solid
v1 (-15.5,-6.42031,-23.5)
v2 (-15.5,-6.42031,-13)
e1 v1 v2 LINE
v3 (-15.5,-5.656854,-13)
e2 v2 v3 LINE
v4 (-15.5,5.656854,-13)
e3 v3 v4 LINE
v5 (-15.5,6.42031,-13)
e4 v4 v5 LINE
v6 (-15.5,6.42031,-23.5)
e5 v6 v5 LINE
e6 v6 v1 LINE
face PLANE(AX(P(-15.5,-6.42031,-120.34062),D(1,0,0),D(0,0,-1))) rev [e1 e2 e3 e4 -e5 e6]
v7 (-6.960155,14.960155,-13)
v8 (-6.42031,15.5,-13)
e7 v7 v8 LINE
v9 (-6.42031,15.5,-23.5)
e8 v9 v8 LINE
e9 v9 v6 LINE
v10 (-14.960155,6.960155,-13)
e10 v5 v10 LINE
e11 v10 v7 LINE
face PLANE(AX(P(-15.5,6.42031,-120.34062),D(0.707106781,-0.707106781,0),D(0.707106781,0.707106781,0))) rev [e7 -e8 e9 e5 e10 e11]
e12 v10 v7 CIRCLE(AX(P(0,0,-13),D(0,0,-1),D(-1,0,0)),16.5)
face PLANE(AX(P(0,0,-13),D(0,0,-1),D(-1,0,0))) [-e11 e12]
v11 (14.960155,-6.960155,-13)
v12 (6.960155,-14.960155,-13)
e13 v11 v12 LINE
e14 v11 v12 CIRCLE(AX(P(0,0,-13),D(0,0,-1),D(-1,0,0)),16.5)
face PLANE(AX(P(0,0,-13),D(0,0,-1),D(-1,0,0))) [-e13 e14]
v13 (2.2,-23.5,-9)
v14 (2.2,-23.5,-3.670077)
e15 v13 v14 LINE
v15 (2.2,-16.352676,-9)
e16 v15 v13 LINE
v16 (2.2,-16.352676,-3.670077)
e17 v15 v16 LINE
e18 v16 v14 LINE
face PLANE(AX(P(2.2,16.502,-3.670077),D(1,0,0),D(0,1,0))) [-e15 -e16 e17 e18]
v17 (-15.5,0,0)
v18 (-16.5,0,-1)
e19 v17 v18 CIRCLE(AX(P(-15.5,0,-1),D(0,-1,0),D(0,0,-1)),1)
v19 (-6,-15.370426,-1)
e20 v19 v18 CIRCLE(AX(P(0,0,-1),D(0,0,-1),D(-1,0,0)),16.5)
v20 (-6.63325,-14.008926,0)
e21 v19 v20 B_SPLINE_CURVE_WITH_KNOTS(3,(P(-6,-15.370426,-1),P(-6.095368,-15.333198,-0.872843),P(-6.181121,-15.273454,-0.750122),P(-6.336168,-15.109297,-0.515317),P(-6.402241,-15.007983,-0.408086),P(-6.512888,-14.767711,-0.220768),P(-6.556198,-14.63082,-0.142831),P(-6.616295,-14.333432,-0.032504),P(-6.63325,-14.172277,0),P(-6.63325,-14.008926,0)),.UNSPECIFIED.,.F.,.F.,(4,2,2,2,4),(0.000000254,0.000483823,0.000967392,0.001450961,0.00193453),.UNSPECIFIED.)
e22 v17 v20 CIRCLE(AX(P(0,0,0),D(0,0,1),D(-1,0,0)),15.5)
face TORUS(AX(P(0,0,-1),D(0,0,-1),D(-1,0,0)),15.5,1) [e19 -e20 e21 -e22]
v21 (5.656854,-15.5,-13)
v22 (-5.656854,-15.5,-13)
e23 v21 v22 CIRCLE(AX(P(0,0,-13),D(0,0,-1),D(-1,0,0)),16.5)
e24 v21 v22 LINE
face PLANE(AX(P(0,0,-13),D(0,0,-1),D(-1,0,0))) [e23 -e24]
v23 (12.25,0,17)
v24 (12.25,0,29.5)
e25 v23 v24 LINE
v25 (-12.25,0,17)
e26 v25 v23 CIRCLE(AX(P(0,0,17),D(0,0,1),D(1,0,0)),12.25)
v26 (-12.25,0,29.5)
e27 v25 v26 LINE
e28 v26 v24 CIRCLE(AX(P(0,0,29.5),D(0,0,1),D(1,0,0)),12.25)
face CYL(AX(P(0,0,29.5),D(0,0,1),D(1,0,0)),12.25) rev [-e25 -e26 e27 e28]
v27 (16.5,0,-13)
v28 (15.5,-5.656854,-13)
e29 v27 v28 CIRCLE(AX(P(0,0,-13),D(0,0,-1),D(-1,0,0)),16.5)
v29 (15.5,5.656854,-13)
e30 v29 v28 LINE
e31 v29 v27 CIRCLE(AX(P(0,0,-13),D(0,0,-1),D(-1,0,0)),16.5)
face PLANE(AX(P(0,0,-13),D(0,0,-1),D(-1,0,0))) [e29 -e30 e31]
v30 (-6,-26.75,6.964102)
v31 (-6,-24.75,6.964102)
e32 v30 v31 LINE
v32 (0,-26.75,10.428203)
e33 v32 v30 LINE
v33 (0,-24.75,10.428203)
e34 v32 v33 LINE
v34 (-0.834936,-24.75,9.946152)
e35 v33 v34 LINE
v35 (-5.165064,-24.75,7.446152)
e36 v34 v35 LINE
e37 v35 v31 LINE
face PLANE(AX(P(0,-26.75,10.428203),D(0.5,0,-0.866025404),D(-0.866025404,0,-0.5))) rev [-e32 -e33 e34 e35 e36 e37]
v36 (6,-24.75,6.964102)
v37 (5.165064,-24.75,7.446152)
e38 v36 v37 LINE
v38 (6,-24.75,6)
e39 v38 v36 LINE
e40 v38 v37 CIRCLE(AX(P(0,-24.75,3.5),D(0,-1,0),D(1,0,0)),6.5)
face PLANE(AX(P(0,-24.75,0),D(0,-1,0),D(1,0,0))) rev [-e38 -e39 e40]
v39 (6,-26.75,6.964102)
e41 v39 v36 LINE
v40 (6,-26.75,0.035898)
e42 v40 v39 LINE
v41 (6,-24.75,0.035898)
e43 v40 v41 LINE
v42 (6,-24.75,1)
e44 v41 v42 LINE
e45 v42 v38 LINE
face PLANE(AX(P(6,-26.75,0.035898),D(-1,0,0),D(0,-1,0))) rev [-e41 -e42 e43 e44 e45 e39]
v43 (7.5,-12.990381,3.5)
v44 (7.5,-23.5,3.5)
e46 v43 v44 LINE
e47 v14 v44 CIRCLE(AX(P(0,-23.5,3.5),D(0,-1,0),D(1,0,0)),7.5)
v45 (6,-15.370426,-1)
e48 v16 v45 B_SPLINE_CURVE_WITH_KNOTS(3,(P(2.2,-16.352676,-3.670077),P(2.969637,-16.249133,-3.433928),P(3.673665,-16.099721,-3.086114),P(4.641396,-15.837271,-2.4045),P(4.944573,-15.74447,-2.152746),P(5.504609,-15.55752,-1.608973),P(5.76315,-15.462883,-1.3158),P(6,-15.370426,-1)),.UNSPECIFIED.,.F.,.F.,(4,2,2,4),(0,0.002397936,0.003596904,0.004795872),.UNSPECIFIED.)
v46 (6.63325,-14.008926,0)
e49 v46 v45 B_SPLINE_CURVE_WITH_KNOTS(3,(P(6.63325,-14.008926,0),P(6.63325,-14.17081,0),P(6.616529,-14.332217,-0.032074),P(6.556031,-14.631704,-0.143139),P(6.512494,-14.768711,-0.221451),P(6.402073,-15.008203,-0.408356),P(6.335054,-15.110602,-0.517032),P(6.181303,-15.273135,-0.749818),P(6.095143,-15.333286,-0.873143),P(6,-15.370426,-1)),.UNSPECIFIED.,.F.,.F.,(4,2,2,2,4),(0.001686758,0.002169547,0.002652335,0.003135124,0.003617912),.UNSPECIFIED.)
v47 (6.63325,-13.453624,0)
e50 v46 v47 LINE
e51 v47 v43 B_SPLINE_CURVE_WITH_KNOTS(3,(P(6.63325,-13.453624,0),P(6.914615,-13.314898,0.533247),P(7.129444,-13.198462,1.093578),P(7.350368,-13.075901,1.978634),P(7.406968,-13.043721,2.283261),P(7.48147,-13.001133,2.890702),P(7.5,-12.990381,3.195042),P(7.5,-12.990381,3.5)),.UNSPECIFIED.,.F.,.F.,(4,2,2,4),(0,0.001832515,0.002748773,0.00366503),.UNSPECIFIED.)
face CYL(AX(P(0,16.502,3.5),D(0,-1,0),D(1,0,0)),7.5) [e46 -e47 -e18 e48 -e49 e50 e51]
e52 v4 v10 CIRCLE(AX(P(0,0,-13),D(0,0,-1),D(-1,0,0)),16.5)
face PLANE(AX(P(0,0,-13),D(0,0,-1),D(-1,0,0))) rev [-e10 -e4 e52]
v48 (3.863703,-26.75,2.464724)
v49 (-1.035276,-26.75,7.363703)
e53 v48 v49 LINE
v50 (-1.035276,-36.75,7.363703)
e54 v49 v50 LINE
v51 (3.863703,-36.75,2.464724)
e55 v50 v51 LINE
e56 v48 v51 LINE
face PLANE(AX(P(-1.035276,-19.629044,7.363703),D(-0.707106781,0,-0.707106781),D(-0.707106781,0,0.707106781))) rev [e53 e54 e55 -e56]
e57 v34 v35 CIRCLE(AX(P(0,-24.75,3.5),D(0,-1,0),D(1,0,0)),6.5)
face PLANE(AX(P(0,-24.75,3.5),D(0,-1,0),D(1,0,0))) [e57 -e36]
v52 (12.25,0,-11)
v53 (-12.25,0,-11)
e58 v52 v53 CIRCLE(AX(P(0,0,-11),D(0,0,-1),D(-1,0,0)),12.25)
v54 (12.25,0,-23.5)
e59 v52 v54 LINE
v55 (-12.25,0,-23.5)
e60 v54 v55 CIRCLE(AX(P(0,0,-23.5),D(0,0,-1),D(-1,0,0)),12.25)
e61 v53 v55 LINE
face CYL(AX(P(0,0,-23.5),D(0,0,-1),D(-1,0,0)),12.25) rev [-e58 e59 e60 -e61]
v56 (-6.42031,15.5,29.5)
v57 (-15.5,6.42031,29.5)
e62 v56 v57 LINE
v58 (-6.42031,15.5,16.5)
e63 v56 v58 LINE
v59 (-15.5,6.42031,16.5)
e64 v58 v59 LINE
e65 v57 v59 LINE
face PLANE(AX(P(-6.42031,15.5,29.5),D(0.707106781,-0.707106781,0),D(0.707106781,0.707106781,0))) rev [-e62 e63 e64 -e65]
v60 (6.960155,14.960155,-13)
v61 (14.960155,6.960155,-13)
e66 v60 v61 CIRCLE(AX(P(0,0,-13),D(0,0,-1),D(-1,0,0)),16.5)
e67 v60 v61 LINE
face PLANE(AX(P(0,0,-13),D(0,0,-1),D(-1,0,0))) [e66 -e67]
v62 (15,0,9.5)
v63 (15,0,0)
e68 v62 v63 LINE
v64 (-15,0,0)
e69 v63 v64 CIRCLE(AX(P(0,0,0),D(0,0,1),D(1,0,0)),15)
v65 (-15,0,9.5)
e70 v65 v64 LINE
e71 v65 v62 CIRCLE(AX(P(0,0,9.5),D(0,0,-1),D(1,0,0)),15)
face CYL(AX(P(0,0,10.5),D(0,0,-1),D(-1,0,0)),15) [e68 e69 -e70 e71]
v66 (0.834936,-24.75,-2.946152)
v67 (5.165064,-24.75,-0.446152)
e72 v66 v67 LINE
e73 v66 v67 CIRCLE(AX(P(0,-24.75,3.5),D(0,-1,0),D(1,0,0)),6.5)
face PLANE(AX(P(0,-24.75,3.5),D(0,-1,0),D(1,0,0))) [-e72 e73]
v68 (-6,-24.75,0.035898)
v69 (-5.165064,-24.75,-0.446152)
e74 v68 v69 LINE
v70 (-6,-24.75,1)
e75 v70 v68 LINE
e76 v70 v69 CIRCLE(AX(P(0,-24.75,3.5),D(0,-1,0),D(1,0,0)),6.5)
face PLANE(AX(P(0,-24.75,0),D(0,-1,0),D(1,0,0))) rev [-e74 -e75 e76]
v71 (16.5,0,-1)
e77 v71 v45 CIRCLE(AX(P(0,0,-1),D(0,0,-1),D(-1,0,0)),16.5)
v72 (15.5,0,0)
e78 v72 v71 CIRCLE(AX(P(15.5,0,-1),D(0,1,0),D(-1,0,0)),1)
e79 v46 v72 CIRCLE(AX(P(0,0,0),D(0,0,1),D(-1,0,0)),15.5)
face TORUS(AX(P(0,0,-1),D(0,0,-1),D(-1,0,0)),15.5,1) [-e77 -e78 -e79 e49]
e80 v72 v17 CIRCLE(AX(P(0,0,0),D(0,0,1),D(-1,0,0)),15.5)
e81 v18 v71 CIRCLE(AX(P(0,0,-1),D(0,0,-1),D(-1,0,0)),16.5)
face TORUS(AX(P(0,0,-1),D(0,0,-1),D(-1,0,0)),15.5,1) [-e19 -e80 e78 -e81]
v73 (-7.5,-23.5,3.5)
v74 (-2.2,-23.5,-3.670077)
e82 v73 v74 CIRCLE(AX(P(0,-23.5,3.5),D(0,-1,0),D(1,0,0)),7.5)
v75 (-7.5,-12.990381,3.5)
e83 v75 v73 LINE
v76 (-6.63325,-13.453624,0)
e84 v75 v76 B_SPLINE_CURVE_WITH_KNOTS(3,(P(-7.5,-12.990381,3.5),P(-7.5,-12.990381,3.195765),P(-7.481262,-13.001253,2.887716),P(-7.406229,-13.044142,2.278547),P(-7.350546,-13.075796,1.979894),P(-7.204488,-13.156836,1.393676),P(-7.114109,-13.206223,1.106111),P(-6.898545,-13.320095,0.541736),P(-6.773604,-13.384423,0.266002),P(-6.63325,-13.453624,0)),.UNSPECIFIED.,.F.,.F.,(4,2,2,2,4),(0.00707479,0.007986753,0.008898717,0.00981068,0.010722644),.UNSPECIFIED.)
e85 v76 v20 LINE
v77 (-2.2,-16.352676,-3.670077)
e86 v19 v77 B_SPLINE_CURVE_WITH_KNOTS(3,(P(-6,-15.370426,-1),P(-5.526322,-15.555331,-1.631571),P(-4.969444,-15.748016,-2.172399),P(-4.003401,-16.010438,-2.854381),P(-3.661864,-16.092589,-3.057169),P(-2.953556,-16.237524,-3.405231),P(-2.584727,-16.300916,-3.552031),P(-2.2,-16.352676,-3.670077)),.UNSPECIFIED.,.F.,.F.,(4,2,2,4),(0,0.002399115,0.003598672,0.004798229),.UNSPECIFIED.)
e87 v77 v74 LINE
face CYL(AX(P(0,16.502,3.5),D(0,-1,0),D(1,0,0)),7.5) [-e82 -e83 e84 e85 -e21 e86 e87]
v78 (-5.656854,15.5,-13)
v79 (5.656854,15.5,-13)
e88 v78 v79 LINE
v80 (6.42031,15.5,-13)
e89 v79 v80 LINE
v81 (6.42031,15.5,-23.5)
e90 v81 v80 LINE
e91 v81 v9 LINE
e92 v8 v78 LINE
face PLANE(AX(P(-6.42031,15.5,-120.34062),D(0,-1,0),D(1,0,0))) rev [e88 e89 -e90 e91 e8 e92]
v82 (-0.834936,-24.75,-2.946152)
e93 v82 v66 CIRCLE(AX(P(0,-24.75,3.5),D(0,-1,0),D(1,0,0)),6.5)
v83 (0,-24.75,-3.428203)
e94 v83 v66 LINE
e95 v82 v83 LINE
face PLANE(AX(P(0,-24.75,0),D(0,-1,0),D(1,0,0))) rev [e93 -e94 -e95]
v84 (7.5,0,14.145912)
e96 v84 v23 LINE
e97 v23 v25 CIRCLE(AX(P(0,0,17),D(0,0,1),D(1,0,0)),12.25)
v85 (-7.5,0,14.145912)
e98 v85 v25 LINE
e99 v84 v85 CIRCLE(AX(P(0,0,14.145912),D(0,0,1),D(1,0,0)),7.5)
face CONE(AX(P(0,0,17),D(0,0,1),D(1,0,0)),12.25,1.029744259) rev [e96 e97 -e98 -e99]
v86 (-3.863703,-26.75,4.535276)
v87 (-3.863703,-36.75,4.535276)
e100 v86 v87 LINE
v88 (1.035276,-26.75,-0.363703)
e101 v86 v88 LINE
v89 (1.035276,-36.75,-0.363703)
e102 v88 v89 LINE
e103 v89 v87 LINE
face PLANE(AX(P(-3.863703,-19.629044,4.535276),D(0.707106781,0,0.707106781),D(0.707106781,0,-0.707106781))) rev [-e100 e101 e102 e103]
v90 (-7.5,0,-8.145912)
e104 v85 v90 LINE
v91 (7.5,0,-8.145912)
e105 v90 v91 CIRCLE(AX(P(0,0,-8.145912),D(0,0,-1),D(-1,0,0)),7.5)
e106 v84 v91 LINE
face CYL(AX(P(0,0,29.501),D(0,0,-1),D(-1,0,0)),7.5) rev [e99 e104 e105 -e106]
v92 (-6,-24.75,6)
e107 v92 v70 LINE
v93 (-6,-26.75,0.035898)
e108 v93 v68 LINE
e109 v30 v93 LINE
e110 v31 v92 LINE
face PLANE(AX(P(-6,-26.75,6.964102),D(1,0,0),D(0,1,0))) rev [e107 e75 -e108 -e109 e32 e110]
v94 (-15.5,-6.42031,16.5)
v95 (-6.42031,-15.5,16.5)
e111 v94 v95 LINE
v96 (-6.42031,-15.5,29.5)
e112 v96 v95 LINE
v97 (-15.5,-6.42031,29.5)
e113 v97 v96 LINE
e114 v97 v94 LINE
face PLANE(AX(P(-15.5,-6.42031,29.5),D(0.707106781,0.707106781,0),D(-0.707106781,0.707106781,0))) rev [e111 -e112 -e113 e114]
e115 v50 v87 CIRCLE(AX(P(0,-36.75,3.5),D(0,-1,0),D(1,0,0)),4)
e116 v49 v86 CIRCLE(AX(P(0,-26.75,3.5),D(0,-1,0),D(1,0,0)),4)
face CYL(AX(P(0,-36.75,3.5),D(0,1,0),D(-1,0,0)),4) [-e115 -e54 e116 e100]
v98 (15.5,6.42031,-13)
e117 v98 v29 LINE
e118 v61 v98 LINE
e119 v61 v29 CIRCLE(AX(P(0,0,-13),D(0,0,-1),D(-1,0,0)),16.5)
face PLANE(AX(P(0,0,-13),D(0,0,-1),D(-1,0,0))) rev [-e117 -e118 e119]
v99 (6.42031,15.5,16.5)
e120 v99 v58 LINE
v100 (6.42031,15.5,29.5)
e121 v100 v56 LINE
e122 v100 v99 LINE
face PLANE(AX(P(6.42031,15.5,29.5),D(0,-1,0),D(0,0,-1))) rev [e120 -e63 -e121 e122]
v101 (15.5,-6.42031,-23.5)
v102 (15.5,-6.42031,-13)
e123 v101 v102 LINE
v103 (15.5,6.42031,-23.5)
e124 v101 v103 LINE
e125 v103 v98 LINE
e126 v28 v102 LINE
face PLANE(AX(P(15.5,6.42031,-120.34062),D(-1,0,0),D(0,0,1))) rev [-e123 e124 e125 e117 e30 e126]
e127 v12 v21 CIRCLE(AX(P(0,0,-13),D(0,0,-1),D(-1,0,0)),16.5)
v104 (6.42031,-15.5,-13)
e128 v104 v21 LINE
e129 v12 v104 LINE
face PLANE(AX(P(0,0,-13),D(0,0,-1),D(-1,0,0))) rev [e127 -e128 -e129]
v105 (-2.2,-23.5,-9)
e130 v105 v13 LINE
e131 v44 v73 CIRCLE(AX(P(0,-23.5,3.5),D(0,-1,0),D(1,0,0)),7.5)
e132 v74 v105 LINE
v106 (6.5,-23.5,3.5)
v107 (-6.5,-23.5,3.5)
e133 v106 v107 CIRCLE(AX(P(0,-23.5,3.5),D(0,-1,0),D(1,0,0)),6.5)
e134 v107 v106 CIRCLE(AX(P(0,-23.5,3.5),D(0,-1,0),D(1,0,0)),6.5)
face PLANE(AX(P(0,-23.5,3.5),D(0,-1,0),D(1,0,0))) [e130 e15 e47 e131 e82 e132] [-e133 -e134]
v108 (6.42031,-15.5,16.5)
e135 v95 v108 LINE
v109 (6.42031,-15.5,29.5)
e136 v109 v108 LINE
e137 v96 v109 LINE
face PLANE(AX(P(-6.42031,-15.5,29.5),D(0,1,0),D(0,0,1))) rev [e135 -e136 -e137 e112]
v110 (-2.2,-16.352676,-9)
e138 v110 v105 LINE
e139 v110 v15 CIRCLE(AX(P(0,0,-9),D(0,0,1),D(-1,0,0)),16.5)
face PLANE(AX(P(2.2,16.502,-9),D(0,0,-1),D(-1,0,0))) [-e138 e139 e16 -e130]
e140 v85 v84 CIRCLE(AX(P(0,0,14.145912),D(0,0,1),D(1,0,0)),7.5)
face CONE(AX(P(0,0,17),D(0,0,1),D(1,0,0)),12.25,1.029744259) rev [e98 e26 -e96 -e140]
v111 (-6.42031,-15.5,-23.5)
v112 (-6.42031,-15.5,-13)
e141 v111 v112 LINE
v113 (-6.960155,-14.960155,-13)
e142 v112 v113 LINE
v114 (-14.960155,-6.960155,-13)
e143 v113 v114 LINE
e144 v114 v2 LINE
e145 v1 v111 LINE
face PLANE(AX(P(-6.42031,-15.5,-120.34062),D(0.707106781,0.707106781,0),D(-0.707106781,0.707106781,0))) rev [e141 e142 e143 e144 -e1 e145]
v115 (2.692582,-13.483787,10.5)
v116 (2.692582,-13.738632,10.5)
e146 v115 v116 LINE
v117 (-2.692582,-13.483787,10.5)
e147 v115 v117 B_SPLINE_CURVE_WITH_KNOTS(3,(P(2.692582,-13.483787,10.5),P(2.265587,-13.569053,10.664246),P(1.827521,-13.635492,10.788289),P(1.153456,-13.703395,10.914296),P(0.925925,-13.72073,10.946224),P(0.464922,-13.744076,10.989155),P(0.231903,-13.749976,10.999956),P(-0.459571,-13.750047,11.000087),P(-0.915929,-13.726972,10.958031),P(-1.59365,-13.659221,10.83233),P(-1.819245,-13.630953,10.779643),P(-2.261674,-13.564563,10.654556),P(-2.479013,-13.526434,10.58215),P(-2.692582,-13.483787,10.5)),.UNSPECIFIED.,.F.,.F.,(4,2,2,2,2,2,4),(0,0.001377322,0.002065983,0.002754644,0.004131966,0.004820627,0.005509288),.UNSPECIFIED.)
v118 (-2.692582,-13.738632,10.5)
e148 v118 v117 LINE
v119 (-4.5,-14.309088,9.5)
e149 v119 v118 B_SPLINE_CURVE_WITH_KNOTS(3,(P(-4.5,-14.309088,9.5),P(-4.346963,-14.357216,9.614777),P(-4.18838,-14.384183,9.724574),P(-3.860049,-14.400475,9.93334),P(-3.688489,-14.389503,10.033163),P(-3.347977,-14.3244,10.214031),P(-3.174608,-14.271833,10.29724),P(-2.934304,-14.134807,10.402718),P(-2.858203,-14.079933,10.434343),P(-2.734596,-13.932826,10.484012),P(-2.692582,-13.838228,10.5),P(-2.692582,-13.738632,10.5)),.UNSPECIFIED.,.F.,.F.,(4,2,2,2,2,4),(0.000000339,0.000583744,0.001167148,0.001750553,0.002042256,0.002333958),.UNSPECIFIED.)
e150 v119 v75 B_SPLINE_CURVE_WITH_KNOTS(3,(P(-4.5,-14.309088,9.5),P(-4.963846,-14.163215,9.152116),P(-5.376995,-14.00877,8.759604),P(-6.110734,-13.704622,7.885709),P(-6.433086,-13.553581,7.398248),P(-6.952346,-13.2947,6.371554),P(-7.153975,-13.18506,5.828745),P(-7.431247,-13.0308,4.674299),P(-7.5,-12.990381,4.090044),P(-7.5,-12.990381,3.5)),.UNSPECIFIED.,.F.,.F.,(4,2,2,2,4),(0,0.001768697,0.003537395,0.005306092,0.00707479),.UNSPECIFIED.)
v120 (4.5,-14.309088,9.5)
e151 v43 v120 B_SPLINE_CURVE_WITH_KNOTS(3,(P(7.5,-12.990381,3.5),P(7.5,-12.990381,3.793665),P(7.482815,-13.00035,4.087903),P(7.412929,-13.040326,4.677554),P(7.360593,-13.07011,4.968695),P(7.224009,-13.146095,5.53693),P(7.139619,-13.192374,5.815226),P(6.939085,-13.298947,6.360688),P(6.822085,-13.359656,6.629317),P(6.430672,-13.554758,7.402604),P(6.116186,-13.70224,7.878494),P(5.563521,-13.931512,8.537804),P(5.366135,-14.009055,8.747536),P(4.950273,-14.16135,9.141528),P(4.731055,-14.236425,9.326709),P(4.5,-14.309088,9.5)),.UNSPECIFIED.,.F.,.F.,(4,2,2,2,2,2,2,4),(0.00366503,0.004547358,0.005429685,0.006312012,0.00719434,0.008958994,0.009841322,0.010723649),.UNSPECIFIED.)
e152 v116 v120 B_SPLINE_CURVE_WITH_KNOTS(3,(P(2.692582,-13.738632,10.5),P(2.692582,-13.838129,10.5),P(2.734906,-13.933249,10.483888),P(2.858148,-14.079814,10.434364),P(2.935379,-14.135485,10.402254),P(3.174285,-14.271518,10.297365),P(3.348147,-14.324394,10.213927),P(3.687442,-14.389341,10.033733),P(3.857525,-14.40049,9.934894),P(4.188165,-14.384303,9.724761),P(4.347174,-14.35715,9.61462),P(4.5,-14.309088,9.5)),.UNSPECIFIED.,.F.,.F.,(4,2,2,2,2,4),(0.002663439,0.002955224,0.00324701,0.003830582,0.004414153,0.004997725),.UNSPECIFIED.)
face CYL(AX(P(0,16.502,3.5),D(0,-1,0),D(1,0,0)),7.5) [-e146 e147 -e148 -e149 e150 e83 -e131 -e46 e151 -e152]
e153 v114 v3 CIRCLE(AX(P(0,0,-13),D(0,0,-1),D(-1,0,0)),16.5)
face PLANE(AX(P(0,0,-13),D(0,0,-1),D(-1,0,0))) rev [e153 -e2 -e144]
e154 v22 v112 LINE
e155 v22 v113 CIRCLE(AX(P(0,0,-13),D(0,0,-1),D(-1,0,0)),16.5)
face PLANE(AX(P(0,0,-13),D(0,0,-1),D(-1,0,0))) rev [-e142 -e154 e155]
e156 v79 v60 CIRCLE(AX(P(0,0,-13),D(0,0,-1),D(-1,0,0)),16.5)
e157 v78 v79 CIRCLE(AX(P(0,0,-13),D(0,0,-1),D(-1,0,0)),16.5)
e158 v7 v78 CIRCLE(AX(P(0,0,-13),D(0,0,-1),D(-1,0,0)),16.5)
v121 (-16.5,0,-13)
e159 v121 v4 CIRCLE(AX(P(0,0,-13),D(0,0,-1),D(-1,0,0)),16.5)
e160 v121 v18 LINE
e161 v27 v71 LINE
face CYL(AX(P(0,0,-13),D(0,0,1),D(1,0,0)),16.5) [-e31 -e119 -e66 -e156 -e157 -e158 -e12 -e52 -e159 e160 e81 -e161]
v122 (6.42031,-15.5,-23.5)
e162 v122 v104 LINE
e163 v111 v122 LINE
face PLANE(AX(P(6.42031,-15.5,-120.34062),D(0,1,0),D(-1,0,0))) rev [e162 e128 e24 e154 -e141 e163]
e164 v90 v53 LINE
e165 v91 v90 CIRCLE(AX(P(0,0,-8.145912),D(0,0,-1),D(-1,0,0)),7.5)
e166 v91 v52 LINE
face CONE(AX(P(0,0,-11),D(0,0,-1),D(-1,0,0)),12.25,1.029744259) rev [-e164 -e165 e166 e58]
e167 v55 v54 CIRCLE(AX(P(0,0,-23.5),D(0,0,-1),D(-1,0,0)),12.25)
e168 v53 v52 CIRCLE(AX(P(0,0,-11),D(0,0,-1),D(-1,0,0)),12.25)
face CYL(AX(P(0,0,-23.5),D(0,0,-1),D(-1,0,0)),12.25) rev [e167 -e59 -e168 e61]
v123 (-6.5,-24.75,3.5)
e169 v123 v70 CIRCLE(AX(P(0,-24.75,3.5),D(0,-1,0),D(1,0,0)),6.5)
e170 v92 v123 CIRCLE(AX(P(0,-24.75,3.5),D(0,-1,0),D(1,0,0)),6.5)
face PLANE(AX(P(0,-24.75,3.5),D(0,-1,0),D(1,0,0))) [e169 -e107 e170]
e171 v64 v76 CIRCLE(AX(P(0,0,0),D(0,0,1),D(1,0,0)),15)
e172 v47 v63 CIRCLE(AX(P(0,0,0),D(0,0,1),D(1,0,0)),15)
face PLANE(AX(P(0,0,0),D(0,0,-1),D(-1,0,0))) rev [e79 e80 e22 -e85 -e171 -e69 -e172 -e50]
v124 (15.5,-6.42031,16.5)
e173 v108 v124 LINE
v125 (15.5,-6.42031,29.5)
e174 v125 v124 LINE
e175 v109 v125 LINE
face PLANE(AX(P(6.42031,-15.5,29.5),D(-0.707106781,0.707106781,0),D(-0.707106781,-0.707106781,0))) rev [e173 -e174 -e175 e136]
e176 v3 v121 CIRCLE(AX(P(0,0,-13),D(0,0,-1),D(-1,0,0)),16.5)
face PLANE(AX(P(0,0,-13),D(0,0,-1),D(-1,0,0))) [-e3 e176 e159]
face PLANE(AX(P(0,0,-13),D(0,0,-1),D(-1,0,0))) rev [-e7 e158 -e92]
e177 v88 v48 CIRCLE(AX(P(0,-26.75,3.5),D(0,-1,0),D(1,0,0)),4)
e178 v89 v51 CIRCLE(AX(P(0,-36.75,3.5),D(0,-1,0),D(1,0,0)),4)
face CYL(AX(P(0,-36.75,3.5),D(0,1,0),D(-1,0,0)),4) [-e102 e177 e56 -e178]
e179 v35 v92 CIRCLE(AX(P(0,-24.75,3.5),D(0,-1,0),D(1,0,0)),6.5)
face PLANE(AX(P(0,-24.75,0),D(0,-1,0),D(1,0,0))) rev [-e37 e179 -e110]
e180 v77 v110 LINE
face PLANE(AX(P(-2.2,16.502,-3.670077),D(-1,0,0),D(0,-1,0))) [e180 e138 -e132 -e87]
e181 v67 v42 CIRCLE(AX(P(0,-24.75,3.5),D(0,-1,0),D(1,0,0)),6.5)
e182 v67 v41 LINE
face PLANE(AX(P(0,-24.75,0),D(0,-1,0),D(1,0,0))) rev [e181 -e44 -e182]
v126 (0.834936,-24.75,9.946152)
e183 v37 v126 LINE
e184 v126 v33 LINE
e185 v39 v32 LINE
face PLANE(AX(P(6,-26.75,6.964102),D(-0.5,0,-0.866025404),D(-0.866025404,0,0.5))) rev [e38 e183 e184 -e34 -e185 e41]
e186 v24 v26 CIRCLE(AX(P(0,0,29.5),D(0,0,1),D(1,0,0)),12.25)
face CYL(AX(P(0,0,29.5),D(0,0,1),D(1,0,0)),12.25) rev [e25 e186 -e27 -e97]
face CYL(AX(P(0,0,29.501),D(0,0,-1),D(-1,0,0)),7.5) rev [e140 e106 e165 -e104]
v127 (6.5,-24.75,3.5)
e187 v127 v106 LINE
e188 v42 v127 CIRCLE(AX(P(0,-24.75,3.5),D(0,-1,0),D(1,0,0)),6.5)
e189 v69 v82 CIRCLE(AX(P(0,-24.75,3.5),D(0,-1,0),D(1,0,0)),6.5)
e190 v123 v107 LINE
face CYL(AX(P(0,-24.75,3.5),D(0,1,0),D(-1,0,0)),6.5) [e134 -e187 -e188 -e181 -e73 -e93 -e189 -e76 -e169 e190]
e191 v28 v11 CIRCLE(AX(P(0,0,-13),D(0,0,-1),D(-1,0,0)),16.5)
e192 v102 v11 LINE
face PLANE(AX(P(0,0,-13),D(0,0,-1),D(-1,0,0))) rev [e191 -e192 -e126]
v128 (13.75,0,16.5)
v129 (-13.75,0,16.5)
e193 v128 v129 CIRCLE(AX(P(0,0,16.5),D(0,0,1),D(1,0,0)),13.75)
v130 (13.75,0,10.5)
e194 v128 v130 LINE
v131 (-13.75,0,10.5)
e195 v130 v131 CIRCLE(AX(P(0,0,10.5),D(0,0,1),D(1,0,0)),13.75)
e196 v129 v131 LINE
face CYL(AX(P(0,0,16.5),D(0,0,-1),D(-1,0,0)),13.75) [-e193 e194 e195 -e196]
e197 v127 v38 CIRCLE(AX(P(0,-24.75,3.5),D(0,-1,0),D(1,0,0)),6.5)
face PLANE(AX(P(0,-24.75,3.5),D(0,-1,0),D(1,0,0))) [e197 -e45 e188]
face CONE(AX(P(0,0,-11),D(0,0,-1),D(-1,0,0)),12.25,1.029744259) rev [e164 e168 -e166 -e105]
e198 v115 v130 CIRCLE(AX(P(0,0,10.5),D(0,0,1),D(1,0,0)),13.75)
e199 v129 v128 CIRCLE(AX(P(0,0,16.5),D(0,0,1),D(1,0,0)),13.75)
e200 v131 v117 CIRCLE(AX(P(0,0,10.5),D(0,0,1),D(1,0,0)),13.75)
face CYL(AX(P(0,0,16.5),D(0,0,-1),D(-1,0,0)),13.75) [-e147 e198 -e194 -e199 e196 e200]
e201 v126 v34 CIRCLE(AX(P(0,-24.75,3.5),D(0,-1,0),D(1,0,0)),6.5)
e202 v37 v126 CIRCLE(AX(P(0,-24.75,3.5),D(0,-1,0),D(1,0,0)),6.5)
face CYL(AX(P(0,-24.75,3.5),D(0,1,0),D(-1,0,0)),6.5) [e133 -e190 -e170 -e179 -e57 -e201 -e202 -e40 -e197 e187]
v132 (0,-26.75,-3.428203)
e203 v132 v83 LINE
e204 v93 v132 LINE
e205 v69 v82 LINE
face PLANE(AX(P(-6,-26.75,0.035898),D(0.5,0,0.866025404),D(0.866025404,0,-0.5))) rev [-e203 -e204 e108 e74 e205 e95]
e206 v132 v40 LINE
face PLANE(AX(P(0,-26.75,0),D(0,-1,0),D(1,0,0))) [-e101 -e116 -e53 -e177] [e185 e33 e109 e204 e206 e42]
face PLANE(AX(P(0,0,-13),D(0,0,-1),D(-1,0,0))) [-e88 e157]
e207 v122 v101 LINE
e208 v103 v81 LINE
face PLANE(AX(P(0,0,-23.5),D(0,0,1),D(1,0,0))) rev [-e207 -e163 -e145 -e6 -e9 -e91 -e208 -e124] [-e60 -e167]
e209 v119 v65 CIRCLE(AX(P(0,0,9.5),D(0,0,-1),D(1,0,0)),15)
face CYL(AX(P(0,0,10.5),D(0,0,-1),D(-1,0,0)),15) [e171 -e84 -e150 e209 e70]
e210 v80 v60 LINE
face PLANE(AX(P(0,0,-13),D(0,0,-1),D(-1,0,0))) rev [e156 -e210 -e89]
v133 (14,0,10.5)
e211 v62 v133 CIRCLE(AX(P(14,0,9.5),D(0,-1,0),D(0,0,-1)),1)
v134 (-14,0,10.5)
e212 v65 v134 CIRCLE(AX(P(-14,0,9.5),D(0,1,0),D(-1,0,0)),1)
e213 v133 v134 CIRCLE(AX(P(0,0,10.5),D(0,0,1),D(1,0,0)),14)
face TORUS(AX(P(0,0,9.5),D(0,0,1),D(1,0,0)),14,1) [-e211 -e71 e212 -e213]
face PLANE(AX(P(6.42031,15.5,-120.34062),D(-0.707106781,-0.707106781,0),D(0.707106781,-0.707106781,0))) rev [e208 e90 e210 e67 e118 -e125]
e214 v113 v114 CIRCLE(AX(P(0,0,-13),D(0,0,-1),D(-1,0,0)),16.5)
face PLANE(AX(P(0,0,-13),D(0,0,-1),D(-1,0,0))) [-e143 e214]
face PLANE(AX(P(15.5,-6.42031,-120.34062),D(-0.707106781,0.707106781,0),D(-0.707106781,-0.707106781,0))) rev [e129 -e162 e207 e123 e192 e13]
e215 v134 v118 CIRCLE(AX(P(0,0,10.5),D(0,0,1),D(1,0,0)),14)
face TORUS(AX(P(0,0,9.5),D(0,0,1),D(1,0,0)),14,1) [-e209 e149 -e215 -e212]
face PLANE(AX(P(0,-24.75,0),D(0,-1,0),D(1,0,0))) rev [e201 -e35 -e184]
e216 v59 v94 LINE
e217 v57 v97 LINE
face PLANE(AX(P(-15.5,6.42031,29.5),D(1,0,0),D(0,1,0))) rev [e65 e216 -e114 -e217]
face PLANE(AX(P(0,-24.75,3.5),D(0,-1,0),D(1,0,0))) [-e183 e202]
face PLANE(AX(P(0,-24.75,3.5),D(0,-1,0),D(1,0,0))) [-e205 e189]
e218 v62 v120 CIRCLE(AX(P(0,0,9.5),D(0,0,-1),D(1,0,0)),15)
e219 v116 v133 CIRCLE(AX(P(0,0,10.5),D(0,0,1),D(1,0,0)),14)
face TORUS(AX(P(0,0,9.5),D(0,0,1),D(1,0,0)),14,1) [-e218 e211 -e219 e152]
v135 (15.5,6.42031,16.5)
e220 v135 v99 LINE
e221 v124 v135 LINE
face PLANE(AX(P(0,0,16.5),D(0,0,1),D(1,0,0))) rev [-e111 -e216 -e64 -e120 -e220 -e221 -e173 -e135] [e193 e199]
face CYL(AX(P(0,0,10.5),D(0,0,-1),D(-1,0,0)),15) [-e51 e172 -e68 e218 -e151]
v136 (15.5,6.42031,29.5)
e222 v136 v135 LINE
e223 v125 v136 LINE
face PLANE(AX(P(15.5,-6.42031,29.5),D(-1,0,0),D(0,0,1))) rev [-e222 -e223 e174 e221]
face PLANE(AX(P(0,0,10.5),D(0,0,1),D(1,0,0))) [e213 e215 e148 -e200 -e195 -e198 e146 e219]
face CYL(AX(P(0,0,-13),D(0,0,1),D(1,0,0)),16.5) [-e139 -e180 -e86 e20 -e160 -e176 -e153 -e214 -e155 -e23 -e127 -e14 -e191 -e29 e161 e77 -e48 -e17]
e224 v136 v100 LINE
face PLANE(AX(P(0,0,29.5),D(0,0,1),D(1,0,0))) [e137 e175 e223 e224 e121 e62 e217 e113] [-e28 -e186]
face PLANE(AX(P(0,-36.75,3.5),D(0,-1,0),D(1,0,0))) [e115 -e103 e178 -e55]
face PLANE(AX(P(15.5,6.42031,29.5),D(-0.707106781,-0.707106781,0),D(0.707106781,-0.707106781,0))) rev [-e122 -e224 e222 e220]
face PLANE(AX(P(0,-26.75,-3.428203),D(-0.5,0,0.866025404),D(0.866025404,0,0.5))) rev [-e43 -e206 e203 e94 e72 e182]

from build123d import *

# Parameters (mm, degrees)
SKETCH_1_R               = 15
EXTRUDE_1_DEPTH          = 10.5
SKETCH_2_R               = 13.75
EXTRUDE_2_DEPTH          = 6
EXTRUDE_3_DEPTH          = 13
SKETCH_4_R               = 16.5
EXTRUDE_4_DEPTH          = 13
EXTRUDE_5_DEPTH          = 10.5
FILLET_1_R               = 1
HOLE_WIZARD_G3_4_1_D     = 24.5
HOLE_WIZARD_G3_4_1_DEPTH = 12.5
HOLE_WIZARD_G3_4_1_TIP   = 7.360542583
HOLE_WIZARD_G3_4_2_D     = 24.5
HOLE_WIZARD_G3_4_2_DEPTH = 12.5
HOLE_WIZARD_G3_4_2_TIP   = 7.360542583
CUT_EXTRUDE_1_REACH      = 59.909
SKETCH_11_R              = 7.5
EXTRUDE_6_REACH          = 54.369
SKETCH_13_R              = 6.5
EXTRUDE_7_DEPTH          = 1.25
EXTRUDE_8_DEPTH          = 2
SKETCH_15_R              = 4
EXTRUDE_9_DEPTH          = 10
CUT_EXTRUDE_START        = -10
CUT_EXTRUDE_2_DEPTH      = 10


with BuildPart() as part:
    # 草图1 → 凸台-拉伸1 (new body)
    with BuildSketch(Plane.XY):
        with Locations(Location((0, 0, 0), (0, 0, 180))):
            Circle(SKETCH_1_R)
    extrude(amount=EXTRUDE_1_DEPTH)

    # 草图2 → 凸台-拉伸2 (add)
    with BuildSketch(Plane.XY.offset(10.5)):
        Circle(SKETCH_2_R)
    extrude(amount=EXTRUDE_2_DEPTH)

    # 草图3 → 凸台-拉伸3 (add)
    with BuildSketch(Plane.XY.offset(16.5)):
        Polygon((6.420310217, -15.5), (15.5, -6.420310217), (15.5, 6.420310217), (6.420310217, 15.5), (-6.420310217, 15.5), (-15.5, 6.420310217), (-15.5, -6.420310217), (-6.420310217, -15.5), align=None)
    extrude(amount=EXTRUDE_3_DEPTH)

    # 草图4 → 凸台-拉伸4 (add)
    with BuildSketch(Plane(origin=(0, 0, 0), x_dir=(-1, 0, 0), z_dir=(0, 0, -1))):
        with Locations(Location((0, 0, 0), (0, 0, 180))):
            Circle(SKETCH_4_R)
    extrude(amount=EXTRUDE_4_DEPTH)

    # 草图6 → 凸台-拉伸5 (add)
    with BuildSketch(Plane(origin=(0, 0, -13), x_dir=(-1, 0, 0), z_dir=(0, 0, -1))):
        Polygon((15.5, -6.420310217), (15.5, 6.420310217), (6.420310217, 15.5), (-6.420310217, 15.5), (-15.5, 6.420310217), (-15.5, -6.420310217), (-6.420310217, -15.5), (6.420310217, -15.5), align=None)
    extrude(amount=EXTRUDE_5_DEPTH)

    # 圆角1
    fillet_1_edges = [part.edges().sort_by_distance(p)[0] for p in [
        (-16.5, 0, 0),
        (15, 0, 10.5),
    ]]
    fillet(fillet_1_edges, radius=FILLET_1_R)

    # G3/4 螺纹孔1
    with Locations(Plane.XY.offset(29.5)):
        with Locations((0, 0)):
            Hole(HOLE_WIZARD_G3_4_1_D / 2, depth=HOLE_WIZARD_G3_4_1_DEPTH)
            with Locations((0, 0, -(HOLE_WIZARD_G3_4_1_DEPTH + HOLE_WIZARD_G3_4_1_TIP / 2))):  # 118° drill point
                Cone(0, HOLE_WIZARD_G3_4_1_D / 2, HOLE_WIZARD_G3_4_1_TIP, mode=Mode.SUBTRACT)

    # G3/4 螺纹孔2
    with Locations(Plane(origin=(0, 0, -23.5), x_dir=(-1, 0, 0), z_dir=(0, 0, -1))):
        with Locations((0, 0)):
            Hole(HOLE_WIZARD_G3_4_2_D / 2, depth=HOLE_WIZARD_G3_4_2_DEPTH)
            with Locations((0, 0, -(HOLE_WIZARD_G3_4_2_DEPTH + HOLE_WIZARD_G3_4_2_TIP / 2))):  # 118° drill point
                Cone(0, HOLE_WIZARD_G3_4_2_D / 2, HOLE_WIZARD_G3_4_2_TIP, mode=Mode.SUBTRACT)

    # 切除-拉伸1: up to this cone (the profile starts outside it)
    cut_extrude_1_end = Plane(origin=(0, 0, -23.5), z_dir=(0, 0, 1)).offset(33.139458417) * Cone(1.664e-06, 45.384140214, 27.269541583, align=(Align.CENTER, Align.CENTER, Align.MIN), mode=Mode.PRIVATE)
    # 草图11 → 切除-拉伸1 (cut, up to the surface)
    with BuildSketch(Plane(origin=(0, 0, -23.5), x_dir=(-1, 0, 0), z_dir=(0, 0, -1)), mode=Mode.PRIVATE) as cut_extrude_1_sk1:
        Circle(SKETCH_11_R)
    cut_extrude_1_tool1 = extrude(cut_extrude_1_sk1.sketch, amount=-CUT_EXTRUDE_1_REACH, mode=Mode.PRIVATE) - cut_extrude_1_end
    add(cut_extrude_1_tool1.solids().sort_by_distance((0, 0, -23.5))[0], mode=Mode.SUBTRACT)

    # 草图12 → 凸台-拉伸6 (add, up to next)
    with BuildSketch(Plane(origin=(0, -23.5, 0), x_dir=(-1, 0, 0), z_dir=(0, -1, 0)), mode=Mode.PRIVATE) as extrude_6_sk1:
        with BuildLine():
            Line((-2.2, 9), (2.2, 9))
            Line((2.2, 9), (2.2, 3.670076708))
            ThreePointArc((2.2, 3.670076708), (0, -11), (-2.2, 3.670076708))
            Line((-2.2, 3.670076708), (-2.2, 9))
        make_face()
    extrude_6_tool1 = extrude(extrude_6_sk1.sketch, amount=-EXTRUDE_6_REACH, mode=Mode.PRIVATE) - part.part
    add(extrude_6_tool1.solids().sort_by_distance((0, -23.5, 2.377731))[0])

    # 草图13 → 凸台-拉伸7 (add)
    with BuildSketch(Plane.XZ.offset(23.5)):
        with Locations((0, 3.5)):
            Circle(SKETCH_13_R)
    extrude(amount=EXTRUDE_7_DEPTH)

    # 草图14 → 凸台-拉伸8 (add)
    with BuildSketch(Plane.XZ.offset(24.75)):
        Polygon((6, 6.964101615), (0, 10.42820323), (-6, 6.964101615), (-6, 0.035898385), (0, -3.42820323), (6, 0.035898385), align=None)
    extrude(amount=EXTRUDE_8_DEPTH)

    # 草图15 → 凸台-拉伸9 (add)
    with BuildSketch(Plane.XZ.offset(26.75)):
        with Locations((0, 3.5)):
            Circle(SKETCH_15_R)
    extrude(amount=EXTRUDE_9_DEPTH)

    # 草图16 → 切除-拉伸2 (cut)
    with BuildSketch(Plane.XZ.offset(36.75).offset(CUT_EXTRUDE_START)):
        with BuildLine():
            Line((-3.863703305, 4.53527618), (1.03527618, -0.363703305))
            ThreePointArc((1.03527618, -0.363703305), (-2.828427125, 0.671572875), (-3.863703305, 4.53527618))
        make_face()
        with BuildLine():
            Line((-1.03527618, 7.363703305), (3.863703305, 2.46472382))
            ThreePointArc((3.863703305, 2.46472382), (2.828427125, 6.328427125), (-1.03527618, 7.363703305))
        make_face()
    extrude(amount=CUT_EXTRUDE_2_DEPTH, mode=Mode.SUBTRACT)


solid = part.part
